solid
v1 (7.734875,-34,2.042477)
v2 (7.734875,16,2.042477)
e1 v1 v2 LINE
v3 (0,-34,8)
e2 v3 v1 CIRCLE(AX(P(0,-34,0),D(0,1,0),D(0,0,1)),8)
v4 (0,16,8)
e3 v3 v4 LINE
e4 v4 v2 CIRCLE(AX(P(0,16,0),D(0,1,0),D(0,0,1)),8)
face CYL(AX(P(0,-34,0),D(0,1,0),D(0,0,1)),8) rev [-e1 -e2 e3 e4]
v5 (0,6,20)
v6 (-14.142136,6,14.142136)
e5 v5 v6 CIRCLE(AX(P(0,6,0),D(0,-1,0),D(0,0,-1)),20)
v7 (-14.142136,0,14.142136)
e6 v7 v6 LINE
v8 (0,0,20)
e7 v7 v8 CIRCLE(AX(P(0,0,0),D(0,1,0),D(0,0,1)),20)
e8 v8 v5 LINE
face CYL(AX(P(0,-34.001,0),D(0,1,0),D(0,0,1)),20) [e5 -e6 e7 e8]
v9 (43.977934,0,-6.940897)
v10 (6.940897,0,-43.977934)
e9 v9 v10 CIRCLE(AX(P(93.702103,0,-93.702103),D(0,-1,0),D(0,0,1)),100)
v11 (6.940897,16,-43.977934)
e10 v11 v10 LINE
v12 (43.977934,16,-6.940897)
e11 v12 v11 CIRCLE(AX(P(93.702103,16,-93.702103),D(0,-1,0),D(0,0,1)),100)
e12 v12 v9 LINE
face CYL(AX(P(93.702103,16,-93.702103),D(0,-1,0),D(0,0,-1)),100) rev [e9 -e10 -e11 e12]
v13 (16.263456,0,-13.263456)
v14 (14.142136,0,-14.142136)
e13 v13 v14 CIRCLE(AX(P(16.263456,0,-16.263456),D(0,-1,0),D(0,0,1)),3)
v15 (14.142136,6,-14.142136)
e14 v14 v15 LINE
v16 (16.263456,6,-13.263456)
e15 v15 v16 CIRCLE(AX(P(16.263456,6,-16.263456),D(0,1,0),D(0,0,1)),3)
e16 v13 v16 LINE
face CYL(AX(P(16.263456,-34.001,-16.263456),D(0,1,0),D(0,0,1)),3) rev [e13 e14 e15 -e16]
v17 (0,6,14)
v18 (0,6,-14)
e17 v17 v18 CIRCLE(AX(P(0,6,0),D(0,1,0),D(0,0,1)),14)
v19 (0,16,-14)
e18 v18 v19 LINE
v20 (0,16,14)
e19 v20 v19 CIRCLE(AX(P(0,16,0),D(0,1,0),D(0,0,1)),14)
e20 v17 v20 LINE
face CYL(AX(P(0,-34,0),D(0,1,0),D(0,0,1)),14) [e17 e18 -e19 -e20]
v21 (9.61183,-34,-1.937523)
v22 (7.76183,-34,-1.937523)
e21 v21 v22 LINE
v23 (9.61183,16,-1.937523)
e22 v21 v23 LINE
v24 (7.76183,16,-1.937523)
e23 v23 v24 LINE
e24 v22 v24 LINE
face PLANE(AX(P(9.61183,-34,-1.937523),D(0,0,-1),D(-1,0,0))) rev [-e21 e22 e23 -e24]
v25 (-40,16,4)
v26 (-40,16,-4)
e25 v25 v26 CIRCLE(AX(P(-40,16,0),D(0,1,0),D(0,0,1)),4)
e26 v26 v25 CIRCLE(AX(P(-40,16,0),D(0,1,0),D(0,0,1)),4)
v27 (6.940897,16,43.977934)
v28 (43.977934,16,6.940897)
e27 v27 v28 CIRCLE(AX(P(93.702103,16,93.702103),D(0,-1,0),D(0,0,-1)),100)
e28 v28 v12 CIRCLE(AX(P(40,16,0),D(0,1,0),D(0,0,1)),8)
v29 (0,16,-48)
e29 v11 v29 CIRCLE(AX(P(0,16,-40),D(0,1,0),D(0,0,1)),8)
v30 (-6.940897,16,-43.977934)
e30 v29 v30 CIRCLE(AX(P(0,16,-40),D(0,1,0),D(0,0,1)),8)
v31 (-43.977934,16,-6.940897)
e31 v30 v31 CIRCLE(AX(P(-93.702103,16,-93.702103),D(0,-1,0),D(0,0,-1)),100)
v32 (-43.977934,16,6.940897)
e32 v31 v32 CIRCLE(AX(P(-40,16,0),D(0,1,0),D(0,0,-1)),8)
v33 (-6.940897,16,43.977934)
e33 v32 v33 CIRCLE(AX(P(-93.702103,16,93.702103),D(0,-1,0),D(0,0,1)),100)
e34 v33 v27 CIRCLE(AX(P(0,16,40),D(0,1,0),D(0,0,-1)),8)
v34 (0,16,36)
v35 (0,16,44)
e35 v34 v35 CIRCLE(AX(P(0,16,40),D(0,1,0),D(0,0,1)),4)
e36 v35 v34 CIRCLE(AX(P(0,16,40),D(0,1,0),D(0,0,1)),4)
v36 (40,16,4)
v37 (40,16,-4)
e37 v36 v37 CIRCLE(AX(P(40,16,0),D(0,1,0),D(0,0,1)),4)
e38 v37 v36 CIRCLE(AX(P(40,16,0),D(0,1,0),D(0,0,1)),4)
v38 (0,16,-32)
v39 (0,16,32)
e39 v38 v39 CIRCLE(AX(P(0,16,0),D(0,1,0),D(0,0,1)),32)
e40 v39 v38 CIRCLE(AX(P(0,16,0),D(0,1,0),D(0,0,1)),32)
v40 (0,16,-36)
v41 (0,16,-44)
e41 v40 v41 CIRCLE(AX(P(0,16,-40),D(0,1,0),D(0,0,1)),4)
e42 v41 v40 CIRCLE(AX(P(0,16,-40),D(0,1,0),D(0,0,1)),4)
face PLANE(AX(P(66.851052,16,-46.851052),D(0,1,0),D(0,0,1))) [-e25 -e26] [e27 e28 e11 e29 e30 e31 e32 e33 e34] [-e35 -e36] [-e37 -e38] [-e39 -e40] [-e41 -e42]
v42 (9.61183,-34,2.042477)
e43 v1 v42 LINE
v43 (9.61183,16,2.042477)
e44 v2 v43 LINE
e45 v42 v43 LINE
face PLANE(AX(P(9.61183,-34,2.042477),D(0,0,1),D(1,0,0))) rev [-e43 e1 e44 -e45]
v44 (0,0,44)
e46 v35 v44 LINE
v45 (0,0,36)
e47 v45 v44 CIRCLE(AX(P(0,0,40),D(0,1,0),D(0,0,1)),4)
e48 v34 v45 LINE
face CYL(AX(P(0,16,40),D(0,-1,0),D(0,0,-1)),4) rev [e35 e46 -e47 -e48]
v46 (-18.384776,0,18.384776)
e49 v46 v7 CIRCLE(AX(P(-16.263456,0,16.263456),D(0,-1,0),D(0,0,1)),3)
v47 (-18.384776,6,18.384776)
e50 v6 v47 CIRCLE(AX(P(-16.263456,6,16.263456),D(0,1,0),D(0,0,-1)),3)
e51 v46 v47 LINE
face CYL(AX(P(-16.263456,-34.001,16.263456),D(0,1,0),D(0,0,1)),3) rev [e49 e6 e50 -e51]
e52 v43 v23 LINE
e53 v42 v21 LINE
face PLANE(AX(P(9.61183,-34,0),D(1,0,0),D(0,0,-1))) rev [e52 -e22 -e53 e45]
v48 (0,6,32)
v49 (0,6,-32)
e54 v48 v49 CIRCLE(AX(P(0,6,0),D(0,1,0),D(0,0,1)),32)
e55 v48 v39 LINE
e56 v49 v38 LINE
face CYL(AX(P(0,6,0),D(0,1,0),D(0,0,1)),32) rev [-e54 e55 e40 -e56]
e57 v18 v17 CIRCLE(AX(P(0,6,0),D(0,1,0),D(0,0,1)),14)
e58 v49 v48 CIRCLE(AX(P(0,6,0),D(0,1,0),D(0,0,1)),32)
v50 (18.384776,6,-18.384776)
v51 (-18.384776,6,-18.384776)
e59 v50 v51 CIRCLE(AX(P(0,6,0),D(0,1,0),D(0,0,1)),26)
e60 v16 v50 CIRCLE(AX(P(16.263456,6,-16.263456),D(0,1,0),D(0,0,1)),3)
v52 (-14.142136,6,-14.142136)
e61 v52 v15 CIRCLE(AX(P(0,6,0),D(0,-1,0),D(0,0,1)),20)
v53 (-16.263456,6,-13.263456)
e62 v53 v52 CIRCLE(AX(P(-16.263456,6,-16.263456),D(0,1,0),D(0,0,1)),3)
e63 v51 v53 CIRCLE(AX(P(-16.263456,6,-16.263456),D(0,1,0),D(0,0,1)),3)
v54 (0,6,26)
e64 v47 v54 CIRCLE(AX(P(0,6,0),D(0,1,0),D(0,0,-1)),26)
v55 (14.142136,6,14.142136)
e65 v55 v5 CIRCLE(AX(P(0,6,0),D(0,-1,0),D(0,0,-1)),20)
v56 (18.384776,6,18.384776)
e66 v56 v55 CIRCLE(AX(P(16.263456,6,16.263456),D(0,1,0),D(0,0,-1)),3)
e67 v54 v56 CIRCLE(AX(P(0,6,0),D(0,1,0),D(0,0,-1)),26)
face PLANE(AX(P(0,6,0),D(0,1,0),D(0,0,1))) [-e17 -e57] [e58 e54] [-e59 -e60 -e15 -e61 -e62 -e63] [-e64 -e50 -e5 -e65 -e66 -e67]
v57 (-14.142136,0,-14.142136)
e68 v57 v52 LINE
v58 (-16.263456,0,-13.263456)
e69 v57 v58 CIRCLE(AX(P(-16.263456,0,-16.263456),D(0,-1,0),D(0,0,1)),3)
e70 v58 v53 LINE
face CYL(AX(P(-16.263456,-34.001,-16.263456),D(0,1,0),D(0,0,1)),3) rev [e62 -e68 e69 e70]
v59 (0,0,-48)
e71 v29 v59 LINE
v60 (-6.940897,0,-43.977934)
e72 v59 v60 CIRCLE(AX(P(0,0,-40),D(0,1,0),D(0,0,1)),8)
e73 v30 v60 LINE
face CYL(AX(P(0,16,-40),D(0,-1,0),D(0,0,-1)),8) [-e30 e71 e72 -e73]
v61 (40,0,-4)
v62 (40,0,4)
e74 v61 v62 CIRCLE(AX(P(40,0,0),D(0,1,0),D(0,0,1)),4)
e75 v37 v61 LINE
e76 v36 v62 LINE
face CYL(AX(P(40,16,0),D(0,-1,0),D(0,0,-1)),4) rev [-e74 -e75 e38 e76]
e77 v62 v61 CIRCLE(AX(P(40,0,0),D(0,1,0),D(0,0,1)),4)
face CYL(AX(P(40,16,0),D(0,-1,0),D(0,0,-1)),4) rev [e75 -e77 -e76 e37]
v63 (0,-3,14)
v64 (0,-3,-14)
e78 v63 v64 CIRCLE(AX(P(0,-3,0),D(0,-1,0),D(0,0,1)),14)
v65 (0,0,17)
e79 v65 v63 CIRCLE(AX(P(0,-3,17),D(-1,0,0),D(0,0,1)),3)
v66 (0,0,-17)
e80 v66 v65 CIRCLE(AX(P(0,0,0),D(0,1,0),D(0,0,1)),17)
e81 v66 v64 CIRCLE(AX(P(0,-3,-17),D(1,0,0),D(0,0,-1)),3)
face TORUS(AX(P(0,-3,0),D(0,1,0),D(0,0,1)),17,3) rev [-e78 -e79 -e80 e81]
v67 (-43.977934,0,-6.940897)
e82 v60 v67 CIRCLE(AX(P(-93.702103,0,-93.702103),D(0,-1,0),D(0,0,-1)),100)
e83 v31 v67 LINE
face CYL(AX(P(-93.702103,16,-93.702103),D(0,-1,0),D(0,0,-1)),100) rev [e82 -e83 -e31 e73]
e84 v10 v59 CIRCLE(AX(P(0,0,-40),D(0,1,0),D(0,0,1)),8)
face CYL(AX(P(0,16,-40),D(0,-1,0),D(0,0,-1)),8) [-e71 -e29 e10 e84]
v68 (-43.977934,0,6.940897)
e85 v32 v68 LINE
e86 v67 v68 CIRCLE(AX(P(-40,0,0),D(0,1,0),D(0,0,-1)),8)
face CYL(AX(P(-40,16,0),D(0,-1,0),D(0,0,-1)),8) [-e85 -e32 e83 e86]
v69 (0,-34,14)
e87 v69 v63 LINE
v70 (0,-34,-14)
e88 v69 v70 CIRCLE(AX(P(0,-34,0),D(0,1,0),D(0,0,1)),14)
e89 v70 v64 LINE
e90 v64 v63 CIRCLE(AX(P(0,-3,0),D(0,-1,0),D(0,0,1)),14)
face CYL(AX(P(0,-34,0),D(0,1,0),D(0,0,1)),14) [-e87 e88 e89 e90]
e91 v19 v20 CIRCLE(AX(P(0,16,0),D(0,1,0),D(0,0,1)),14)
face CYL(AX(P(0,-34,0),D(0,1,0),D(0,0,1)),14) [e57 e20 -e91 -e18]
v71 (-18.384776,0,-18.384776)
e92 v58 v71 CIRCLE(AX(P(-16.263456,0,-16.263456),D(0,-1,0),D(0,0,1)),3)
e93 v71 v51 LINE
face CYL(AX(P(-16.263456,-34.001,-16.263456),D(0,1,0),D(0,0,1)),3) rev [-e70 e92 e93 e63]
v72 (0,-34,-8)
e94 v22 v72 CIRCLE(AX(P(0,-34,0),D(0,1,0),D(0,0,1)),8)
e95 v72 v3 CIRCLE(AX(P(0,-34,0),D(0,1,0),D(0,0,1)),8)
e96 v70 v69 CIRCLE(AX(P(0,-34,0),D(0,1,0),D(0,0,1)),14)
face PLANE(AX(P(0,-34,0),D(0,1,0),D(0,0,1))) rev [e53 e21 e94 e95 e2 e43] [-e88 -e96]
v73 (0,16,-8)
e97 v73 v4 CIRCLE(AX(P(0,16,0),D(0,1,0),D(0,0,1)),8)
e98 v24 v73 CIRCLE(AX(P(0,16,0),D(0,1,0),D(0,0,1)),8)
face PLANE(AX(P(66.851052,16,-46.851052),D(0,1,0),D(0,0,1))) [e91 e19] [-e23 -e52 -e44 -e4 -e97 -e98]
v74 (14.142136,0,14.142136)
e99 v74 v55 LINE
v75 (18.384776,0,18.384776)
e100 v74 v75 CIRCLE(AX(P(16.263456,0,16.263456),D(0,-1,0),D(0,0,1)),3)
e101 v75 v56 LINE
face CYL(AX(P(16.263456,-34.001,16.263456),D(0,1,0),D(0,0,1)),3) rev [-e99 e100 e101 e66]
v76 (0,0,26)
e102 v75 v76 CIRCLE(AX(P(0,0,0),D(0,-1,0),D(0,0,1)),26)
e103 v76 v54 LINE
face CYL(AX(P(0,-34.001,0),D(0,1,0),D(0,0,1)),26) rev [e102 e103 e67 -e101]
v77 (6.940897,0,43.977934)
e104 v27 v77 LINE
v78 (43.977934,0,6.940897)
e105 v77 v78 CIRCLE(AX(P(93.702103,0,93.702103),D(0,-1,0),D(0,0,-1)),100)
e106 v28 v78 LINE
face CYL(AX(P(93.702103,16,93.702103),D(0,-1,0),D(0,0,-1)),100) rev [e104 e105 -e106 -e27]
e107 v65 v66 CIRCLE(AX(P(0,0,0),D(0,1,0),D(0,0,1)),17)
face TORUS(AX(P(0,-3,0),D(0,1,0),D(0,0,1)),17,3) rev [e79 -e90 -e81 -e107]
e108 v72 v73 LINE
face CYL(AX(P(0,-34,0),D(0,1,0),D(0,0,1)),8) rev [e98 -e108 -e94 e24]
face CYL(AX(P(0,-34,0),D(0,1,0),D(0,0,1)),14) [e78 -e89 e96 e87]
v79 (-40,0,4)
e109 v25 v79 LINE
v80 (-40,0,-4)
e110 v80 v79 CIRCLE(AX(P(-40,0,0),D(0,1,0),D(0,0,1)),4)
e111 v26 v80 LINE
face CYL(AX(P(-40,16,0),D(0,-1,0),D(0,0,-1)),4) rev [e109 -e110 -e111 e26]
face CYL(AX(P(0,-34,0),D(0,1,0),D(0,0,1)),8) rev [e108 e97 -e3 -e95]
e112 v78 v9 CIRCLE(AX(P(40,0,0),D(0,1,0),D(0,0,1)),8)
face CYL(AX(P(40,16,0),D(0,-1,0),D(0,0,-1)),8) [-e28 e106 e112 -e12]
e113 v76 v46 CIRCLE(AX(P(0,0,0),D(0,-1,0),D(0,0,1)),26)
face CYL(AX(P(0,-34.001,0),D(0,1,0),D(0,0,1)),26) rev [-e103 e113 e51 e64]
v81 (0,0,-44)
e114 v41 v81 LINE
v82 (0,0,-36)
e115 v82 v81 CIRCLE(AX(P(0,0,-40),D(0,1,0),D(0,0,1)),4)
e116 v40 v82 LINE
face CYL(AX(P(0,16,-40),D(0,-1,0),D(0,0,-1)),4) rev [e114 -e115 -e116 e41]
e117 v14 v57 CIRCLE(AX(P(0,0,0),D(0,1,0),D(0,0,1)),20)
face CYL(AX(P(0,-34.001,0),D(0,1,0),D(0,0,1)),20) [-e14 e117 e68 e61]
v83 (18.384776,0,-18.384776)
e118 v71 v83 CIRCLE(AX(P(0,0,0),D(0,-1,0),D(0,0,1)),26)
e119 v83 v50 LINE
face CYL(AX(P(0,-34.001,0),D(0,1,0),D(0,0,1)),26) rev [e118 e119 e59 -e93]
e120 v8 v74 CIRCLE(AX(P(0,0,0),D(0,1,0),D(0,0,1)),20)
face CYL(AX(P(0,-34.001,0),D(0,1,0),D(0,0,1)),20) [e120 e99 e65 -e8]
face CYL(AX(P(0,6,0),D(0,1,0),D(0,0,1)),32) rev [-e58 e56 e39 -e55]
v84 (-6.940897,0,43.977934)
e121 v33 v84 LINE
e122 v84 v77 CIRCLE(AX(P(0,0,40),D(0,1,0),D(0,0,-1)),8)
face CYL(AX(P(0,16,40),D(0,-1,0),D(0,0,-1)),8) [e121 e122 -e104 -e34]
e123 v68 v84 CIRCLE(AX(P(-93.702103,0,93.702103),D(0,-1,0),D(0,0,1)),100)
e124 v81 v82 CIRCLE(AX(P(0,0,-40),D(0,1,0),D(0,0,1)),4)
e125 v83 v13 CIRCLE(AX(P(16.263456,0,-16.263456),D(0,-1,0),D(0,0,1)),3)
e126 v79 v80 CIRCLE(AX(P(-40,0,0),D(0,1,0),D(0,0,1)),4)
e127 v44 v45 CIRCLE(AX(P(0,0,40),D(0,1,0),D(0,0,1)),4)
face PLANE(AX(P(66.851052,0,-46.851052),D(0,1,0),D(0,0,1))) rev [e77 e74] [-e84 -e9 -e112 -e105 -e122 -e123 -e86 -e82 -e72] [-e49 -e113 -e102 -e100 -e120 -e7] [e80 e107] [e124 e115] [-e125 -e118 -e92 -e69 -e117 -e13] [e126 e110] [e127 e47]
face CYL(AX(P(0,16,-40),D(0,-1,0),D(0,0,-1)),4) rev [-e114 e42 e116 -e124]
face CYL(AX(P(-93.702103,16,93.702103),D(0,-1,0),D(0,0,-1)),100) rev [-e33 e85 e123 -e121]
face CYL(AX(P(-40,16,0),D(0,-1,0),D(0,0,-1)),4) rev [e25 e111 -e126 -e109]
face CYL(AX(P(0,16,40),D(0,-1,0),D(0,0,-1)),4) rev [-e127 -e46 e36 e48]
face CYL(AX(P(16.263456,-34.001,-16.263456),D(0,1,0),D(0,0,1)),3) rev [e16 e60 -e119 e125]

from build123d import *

# Parameters (mm, degrees)
FLANGE_PROFILE_SKETCH_R       = 4
SQUARE_FLANGE_100X16_DEPTH    = 16
RECESS_SKETCH_64_R            = 32
RECESS_64X10_DEPTH            = 10
HUB_BOSS_28_REACH             = 70.615
HUB_SKETCH_28_R               = 14
HUB_BOSS_28_DIRECTION_2_DEPTH = 40
HUB_FILLET_R3_R               = 3
KEYED_BORE_DEPTH              = 85.308955633
ARC_SLOTS_REACH               = 80.791


with BuildPart() as part:
    # Flange Profile Sketch → Square Flange 100x16 (new body)
    with BuildSketch(Plane(origin=(0, 0, 0), x_dir=(1, 0, 0), z_dir=(0, 1, 0))):
        with BuildLine():
            ThreePointArc((43.977933562, -6.940896525), (48, 0), (43.977933562, 6.940896525))
            ThreePointArc((43.977933562, 6.940896525), (22.991424972, 22.991424972), (6.940896525, 43.977933562))
            ThreePointArc((6.940896525, 43.977933562), (0, 48), (-6.940896525, 43.977933562))
            ThreePointArc((-6.940896525, 43.977933562), (-22.991424972, 22.991424972), (-43.977933562, 6.940896525))
            ThreePointArc((-43.977933562, 6.940896525), (-48, 0), (-43.977933562, -6.940896525))
            ThreePointArc((-43.977933562, -6.940896525), (-22.991424972, -22.991424972), (-6.940896525, -43.977933562))
            ThreePointArc((-6.940896525, -43.977933562), (0, -48), (6.940896525, -43.977933562))
            ThreePointArc((6.940896525, -43.977933562), (22.991424972, -22.991424972), (43.977933562, -6.940896525))
        make_face()
        with Locations(Location((40, 0, 0), (0, 0, 270))):
            Circle(FLANGE_PROFILE_SKETCH_R, mode=Mode.SUBTRACT)
        with Locations(Location((0, -40, 0), (0, 0, 270))):
            Circle(FLANGE_PROFILE_SKETCH_R, mode=Mode.SUBTRACT)
        with Locations(Location((-40, 0, 0), (0, 0, 270))):
            Circle(FLANGE_PROFILE_SKETCH_R, mode=Mode.SUBTRACT)
        with Locations(Location((0, 40, 0), (0, 0, 270))):
            Circle(FLANGE_PROFILE_SKETCH_R, mode=Mode.SUBTRACT)
    extrude(amount=SQUARE_FLANGE_100X16_DEPTH)

    # Recess Sketch Ø64 → Recess Ø64x10 (cut)
    with BuildSketch(Plane(origin=(0, 16, 0), x_dir=(1, 0, 0), z_dir=(0, 1, 0))):
        with Locations(Location((0, 0, 0), (0, 0, 270))):
            Circle(RECESS_SKETCH_64_R)
    extrude(amount=-RECESS_64X10_DEPTH, mode=Mode.SUBTRACT)

    # Hub Boss Ø28: up to this face of the body (flat: up to its plane)
    hub_boss_28_end = Plane(part.part.faces().sort_by_distance((22.895424972, 16, 22.895424972))[0])
    # Hub Sketch Ø28 → Hub Boss Ø28 (add, up to the picked face)
    with BuildSketch(Plane(origin=(0, 6, 0), x_dir=(1, 0, 0), z_dir=(0, 1, 0)), mode=Mode.PRIVATE) as hub_boss_28_sk1:
        with Locations(Location((0, 0, 0), (0, 0, 270))):
            Circle(HUB_SKETCH_28_R)
    hub_boss_28_tool1 = split(extrude(hub_boss_28_sk1.sketch, amount=HUB_BOSS_28_REACH, mode=Mode.PRIVATE), bisect_by=hub_boss_28_end, keep=Keep.BOTH, mode=Mode.PRIVATE)
    add(hub_boss_28_tool1.solids().sort_by(Axis((0, 6, 0), (0, 1, 0)))[0])

    # Hub Sketch Ø28 → Hub Boss Ø28 direction 2 (add)
    with BuildSketch(Plane(origin=(0, 6, 0), x_dir=(1, 0, 0), z_dir=(0, 1, 0))):
        with Locations(Location((0, 0, 0), (0, 0, 270))):
            Circle(HUB_SKETCH_28_R)
    extrude(amount=-HUB_BOSS_28_DIRECTION_2_DEPTH)

    # Hub Fillet R3
    hub_fillet_r3_edges = [part.edges().sort_by_distance(p)[0] for p in [
        (0, 0, -14),
    ]]
    fillet(hub_fillet_r3_edges, radius=HUB_FILLET_R3_R)

    # Keyed Bore Sketch → Keyed Bore (cut, through all)
    with BuildSketch(Plane(origin=(0, 16, 0), x_dir=(1, 0, 0), z_dir=(0, 1, 0))):
        with BuildLine():
            Line((9.611830035, 0), (9.611830035, 1.937522775))
            Line((9.611830035, 1.937522775), (7.761830035, 1.937522775))
            ThreePointArc((7.761830035, 1.937522775), (-7.999816529, 0.054180315), (7.73487471, -2.042477225))
            Line((7.73487471, -2.042477225), (9.611830035, -2.042477225))
            Line((9.611830035, -2.042477225), (9.611830035, 0))
        make_face()
    extrude(amount=-KEYED_BORE_DEPTH, mode=Mode.SUBTRACT)

    # Arc Slots Sketch → Arc Slots (cut, up to next)
    with BuildSketch(Plane(origin=(0, 6, 0), x_dir=(1, 0, 0), z_dir=(0, 1, 0)), mode=Mode.PRIVATE) as arc_slots_sk1:
        with BuildLine():
            ThreePointArc((18.384776311, 18.384776311), (0, 26), (-18.384776311, 18.384776311))
            ThreePointArc((-18.384776311, 18.384776311), (-18.384776311, 14.142135624), (-14.142135624, 14.142135624))
            ThreePointArc((-14.142135624, 14.142135624), (0, 20), (14.142135624, 14.142135624))
            ThreePointArc((14.142135624, 14.142135624), (18.384776311, 14.142135624), (18.384776311, 18.384776311))
        make_face()
    arc_slots_tool1 = extrude(arc_slots_sk1.sketch, amount=-ARC_SLOTS_REACH, mode=Mode.PRIVATE) & part.part
    # Arc Slots Sketch → Arc Slots (cut, up to next)
    with BuildSketch(Plane(origin=(0, 6, 0), x_dir=(1, 0, 0), z_dir=(0, 1, 0)), mode=Mode.PRIVATE) as arc_slots_sk2:
        with BuildLine():
            ThreePointArc((18.384776311, -18.384776311), (0, -26), (-18.384776311, -18.384776311))
            ThreePointArc((-18.384776311, -18.384776311), (-18.384776311, -14.142135624), (-14.142135624, -14.142135624))
            ThreePointArc((-14.142135624, -14.142135624), (0, -20), (14.142135624, -14.142135624))
            ThreePointArc((14.142135624, -14.142135624), (18.384776311, -14.142135624), (18.384776311, -18.384776311))
        make_face()
    arc_slots_tool2 = extrude(arc_slots_sk2.sketch, amount=-ARC_SLOTS_REACH, mode=Mode.PRIVATE) & part.part
    add(arc_slots_tool1.solids().sort_by_distance((0, 6, -20.194527))[0], mode=Mode.SUBTRACT)
    add(arc_slots_tool2.solids().sort_by_distance((0, 6, 20.194527))[0], mode=Mode.SUBTRACT)


solid = part.part
